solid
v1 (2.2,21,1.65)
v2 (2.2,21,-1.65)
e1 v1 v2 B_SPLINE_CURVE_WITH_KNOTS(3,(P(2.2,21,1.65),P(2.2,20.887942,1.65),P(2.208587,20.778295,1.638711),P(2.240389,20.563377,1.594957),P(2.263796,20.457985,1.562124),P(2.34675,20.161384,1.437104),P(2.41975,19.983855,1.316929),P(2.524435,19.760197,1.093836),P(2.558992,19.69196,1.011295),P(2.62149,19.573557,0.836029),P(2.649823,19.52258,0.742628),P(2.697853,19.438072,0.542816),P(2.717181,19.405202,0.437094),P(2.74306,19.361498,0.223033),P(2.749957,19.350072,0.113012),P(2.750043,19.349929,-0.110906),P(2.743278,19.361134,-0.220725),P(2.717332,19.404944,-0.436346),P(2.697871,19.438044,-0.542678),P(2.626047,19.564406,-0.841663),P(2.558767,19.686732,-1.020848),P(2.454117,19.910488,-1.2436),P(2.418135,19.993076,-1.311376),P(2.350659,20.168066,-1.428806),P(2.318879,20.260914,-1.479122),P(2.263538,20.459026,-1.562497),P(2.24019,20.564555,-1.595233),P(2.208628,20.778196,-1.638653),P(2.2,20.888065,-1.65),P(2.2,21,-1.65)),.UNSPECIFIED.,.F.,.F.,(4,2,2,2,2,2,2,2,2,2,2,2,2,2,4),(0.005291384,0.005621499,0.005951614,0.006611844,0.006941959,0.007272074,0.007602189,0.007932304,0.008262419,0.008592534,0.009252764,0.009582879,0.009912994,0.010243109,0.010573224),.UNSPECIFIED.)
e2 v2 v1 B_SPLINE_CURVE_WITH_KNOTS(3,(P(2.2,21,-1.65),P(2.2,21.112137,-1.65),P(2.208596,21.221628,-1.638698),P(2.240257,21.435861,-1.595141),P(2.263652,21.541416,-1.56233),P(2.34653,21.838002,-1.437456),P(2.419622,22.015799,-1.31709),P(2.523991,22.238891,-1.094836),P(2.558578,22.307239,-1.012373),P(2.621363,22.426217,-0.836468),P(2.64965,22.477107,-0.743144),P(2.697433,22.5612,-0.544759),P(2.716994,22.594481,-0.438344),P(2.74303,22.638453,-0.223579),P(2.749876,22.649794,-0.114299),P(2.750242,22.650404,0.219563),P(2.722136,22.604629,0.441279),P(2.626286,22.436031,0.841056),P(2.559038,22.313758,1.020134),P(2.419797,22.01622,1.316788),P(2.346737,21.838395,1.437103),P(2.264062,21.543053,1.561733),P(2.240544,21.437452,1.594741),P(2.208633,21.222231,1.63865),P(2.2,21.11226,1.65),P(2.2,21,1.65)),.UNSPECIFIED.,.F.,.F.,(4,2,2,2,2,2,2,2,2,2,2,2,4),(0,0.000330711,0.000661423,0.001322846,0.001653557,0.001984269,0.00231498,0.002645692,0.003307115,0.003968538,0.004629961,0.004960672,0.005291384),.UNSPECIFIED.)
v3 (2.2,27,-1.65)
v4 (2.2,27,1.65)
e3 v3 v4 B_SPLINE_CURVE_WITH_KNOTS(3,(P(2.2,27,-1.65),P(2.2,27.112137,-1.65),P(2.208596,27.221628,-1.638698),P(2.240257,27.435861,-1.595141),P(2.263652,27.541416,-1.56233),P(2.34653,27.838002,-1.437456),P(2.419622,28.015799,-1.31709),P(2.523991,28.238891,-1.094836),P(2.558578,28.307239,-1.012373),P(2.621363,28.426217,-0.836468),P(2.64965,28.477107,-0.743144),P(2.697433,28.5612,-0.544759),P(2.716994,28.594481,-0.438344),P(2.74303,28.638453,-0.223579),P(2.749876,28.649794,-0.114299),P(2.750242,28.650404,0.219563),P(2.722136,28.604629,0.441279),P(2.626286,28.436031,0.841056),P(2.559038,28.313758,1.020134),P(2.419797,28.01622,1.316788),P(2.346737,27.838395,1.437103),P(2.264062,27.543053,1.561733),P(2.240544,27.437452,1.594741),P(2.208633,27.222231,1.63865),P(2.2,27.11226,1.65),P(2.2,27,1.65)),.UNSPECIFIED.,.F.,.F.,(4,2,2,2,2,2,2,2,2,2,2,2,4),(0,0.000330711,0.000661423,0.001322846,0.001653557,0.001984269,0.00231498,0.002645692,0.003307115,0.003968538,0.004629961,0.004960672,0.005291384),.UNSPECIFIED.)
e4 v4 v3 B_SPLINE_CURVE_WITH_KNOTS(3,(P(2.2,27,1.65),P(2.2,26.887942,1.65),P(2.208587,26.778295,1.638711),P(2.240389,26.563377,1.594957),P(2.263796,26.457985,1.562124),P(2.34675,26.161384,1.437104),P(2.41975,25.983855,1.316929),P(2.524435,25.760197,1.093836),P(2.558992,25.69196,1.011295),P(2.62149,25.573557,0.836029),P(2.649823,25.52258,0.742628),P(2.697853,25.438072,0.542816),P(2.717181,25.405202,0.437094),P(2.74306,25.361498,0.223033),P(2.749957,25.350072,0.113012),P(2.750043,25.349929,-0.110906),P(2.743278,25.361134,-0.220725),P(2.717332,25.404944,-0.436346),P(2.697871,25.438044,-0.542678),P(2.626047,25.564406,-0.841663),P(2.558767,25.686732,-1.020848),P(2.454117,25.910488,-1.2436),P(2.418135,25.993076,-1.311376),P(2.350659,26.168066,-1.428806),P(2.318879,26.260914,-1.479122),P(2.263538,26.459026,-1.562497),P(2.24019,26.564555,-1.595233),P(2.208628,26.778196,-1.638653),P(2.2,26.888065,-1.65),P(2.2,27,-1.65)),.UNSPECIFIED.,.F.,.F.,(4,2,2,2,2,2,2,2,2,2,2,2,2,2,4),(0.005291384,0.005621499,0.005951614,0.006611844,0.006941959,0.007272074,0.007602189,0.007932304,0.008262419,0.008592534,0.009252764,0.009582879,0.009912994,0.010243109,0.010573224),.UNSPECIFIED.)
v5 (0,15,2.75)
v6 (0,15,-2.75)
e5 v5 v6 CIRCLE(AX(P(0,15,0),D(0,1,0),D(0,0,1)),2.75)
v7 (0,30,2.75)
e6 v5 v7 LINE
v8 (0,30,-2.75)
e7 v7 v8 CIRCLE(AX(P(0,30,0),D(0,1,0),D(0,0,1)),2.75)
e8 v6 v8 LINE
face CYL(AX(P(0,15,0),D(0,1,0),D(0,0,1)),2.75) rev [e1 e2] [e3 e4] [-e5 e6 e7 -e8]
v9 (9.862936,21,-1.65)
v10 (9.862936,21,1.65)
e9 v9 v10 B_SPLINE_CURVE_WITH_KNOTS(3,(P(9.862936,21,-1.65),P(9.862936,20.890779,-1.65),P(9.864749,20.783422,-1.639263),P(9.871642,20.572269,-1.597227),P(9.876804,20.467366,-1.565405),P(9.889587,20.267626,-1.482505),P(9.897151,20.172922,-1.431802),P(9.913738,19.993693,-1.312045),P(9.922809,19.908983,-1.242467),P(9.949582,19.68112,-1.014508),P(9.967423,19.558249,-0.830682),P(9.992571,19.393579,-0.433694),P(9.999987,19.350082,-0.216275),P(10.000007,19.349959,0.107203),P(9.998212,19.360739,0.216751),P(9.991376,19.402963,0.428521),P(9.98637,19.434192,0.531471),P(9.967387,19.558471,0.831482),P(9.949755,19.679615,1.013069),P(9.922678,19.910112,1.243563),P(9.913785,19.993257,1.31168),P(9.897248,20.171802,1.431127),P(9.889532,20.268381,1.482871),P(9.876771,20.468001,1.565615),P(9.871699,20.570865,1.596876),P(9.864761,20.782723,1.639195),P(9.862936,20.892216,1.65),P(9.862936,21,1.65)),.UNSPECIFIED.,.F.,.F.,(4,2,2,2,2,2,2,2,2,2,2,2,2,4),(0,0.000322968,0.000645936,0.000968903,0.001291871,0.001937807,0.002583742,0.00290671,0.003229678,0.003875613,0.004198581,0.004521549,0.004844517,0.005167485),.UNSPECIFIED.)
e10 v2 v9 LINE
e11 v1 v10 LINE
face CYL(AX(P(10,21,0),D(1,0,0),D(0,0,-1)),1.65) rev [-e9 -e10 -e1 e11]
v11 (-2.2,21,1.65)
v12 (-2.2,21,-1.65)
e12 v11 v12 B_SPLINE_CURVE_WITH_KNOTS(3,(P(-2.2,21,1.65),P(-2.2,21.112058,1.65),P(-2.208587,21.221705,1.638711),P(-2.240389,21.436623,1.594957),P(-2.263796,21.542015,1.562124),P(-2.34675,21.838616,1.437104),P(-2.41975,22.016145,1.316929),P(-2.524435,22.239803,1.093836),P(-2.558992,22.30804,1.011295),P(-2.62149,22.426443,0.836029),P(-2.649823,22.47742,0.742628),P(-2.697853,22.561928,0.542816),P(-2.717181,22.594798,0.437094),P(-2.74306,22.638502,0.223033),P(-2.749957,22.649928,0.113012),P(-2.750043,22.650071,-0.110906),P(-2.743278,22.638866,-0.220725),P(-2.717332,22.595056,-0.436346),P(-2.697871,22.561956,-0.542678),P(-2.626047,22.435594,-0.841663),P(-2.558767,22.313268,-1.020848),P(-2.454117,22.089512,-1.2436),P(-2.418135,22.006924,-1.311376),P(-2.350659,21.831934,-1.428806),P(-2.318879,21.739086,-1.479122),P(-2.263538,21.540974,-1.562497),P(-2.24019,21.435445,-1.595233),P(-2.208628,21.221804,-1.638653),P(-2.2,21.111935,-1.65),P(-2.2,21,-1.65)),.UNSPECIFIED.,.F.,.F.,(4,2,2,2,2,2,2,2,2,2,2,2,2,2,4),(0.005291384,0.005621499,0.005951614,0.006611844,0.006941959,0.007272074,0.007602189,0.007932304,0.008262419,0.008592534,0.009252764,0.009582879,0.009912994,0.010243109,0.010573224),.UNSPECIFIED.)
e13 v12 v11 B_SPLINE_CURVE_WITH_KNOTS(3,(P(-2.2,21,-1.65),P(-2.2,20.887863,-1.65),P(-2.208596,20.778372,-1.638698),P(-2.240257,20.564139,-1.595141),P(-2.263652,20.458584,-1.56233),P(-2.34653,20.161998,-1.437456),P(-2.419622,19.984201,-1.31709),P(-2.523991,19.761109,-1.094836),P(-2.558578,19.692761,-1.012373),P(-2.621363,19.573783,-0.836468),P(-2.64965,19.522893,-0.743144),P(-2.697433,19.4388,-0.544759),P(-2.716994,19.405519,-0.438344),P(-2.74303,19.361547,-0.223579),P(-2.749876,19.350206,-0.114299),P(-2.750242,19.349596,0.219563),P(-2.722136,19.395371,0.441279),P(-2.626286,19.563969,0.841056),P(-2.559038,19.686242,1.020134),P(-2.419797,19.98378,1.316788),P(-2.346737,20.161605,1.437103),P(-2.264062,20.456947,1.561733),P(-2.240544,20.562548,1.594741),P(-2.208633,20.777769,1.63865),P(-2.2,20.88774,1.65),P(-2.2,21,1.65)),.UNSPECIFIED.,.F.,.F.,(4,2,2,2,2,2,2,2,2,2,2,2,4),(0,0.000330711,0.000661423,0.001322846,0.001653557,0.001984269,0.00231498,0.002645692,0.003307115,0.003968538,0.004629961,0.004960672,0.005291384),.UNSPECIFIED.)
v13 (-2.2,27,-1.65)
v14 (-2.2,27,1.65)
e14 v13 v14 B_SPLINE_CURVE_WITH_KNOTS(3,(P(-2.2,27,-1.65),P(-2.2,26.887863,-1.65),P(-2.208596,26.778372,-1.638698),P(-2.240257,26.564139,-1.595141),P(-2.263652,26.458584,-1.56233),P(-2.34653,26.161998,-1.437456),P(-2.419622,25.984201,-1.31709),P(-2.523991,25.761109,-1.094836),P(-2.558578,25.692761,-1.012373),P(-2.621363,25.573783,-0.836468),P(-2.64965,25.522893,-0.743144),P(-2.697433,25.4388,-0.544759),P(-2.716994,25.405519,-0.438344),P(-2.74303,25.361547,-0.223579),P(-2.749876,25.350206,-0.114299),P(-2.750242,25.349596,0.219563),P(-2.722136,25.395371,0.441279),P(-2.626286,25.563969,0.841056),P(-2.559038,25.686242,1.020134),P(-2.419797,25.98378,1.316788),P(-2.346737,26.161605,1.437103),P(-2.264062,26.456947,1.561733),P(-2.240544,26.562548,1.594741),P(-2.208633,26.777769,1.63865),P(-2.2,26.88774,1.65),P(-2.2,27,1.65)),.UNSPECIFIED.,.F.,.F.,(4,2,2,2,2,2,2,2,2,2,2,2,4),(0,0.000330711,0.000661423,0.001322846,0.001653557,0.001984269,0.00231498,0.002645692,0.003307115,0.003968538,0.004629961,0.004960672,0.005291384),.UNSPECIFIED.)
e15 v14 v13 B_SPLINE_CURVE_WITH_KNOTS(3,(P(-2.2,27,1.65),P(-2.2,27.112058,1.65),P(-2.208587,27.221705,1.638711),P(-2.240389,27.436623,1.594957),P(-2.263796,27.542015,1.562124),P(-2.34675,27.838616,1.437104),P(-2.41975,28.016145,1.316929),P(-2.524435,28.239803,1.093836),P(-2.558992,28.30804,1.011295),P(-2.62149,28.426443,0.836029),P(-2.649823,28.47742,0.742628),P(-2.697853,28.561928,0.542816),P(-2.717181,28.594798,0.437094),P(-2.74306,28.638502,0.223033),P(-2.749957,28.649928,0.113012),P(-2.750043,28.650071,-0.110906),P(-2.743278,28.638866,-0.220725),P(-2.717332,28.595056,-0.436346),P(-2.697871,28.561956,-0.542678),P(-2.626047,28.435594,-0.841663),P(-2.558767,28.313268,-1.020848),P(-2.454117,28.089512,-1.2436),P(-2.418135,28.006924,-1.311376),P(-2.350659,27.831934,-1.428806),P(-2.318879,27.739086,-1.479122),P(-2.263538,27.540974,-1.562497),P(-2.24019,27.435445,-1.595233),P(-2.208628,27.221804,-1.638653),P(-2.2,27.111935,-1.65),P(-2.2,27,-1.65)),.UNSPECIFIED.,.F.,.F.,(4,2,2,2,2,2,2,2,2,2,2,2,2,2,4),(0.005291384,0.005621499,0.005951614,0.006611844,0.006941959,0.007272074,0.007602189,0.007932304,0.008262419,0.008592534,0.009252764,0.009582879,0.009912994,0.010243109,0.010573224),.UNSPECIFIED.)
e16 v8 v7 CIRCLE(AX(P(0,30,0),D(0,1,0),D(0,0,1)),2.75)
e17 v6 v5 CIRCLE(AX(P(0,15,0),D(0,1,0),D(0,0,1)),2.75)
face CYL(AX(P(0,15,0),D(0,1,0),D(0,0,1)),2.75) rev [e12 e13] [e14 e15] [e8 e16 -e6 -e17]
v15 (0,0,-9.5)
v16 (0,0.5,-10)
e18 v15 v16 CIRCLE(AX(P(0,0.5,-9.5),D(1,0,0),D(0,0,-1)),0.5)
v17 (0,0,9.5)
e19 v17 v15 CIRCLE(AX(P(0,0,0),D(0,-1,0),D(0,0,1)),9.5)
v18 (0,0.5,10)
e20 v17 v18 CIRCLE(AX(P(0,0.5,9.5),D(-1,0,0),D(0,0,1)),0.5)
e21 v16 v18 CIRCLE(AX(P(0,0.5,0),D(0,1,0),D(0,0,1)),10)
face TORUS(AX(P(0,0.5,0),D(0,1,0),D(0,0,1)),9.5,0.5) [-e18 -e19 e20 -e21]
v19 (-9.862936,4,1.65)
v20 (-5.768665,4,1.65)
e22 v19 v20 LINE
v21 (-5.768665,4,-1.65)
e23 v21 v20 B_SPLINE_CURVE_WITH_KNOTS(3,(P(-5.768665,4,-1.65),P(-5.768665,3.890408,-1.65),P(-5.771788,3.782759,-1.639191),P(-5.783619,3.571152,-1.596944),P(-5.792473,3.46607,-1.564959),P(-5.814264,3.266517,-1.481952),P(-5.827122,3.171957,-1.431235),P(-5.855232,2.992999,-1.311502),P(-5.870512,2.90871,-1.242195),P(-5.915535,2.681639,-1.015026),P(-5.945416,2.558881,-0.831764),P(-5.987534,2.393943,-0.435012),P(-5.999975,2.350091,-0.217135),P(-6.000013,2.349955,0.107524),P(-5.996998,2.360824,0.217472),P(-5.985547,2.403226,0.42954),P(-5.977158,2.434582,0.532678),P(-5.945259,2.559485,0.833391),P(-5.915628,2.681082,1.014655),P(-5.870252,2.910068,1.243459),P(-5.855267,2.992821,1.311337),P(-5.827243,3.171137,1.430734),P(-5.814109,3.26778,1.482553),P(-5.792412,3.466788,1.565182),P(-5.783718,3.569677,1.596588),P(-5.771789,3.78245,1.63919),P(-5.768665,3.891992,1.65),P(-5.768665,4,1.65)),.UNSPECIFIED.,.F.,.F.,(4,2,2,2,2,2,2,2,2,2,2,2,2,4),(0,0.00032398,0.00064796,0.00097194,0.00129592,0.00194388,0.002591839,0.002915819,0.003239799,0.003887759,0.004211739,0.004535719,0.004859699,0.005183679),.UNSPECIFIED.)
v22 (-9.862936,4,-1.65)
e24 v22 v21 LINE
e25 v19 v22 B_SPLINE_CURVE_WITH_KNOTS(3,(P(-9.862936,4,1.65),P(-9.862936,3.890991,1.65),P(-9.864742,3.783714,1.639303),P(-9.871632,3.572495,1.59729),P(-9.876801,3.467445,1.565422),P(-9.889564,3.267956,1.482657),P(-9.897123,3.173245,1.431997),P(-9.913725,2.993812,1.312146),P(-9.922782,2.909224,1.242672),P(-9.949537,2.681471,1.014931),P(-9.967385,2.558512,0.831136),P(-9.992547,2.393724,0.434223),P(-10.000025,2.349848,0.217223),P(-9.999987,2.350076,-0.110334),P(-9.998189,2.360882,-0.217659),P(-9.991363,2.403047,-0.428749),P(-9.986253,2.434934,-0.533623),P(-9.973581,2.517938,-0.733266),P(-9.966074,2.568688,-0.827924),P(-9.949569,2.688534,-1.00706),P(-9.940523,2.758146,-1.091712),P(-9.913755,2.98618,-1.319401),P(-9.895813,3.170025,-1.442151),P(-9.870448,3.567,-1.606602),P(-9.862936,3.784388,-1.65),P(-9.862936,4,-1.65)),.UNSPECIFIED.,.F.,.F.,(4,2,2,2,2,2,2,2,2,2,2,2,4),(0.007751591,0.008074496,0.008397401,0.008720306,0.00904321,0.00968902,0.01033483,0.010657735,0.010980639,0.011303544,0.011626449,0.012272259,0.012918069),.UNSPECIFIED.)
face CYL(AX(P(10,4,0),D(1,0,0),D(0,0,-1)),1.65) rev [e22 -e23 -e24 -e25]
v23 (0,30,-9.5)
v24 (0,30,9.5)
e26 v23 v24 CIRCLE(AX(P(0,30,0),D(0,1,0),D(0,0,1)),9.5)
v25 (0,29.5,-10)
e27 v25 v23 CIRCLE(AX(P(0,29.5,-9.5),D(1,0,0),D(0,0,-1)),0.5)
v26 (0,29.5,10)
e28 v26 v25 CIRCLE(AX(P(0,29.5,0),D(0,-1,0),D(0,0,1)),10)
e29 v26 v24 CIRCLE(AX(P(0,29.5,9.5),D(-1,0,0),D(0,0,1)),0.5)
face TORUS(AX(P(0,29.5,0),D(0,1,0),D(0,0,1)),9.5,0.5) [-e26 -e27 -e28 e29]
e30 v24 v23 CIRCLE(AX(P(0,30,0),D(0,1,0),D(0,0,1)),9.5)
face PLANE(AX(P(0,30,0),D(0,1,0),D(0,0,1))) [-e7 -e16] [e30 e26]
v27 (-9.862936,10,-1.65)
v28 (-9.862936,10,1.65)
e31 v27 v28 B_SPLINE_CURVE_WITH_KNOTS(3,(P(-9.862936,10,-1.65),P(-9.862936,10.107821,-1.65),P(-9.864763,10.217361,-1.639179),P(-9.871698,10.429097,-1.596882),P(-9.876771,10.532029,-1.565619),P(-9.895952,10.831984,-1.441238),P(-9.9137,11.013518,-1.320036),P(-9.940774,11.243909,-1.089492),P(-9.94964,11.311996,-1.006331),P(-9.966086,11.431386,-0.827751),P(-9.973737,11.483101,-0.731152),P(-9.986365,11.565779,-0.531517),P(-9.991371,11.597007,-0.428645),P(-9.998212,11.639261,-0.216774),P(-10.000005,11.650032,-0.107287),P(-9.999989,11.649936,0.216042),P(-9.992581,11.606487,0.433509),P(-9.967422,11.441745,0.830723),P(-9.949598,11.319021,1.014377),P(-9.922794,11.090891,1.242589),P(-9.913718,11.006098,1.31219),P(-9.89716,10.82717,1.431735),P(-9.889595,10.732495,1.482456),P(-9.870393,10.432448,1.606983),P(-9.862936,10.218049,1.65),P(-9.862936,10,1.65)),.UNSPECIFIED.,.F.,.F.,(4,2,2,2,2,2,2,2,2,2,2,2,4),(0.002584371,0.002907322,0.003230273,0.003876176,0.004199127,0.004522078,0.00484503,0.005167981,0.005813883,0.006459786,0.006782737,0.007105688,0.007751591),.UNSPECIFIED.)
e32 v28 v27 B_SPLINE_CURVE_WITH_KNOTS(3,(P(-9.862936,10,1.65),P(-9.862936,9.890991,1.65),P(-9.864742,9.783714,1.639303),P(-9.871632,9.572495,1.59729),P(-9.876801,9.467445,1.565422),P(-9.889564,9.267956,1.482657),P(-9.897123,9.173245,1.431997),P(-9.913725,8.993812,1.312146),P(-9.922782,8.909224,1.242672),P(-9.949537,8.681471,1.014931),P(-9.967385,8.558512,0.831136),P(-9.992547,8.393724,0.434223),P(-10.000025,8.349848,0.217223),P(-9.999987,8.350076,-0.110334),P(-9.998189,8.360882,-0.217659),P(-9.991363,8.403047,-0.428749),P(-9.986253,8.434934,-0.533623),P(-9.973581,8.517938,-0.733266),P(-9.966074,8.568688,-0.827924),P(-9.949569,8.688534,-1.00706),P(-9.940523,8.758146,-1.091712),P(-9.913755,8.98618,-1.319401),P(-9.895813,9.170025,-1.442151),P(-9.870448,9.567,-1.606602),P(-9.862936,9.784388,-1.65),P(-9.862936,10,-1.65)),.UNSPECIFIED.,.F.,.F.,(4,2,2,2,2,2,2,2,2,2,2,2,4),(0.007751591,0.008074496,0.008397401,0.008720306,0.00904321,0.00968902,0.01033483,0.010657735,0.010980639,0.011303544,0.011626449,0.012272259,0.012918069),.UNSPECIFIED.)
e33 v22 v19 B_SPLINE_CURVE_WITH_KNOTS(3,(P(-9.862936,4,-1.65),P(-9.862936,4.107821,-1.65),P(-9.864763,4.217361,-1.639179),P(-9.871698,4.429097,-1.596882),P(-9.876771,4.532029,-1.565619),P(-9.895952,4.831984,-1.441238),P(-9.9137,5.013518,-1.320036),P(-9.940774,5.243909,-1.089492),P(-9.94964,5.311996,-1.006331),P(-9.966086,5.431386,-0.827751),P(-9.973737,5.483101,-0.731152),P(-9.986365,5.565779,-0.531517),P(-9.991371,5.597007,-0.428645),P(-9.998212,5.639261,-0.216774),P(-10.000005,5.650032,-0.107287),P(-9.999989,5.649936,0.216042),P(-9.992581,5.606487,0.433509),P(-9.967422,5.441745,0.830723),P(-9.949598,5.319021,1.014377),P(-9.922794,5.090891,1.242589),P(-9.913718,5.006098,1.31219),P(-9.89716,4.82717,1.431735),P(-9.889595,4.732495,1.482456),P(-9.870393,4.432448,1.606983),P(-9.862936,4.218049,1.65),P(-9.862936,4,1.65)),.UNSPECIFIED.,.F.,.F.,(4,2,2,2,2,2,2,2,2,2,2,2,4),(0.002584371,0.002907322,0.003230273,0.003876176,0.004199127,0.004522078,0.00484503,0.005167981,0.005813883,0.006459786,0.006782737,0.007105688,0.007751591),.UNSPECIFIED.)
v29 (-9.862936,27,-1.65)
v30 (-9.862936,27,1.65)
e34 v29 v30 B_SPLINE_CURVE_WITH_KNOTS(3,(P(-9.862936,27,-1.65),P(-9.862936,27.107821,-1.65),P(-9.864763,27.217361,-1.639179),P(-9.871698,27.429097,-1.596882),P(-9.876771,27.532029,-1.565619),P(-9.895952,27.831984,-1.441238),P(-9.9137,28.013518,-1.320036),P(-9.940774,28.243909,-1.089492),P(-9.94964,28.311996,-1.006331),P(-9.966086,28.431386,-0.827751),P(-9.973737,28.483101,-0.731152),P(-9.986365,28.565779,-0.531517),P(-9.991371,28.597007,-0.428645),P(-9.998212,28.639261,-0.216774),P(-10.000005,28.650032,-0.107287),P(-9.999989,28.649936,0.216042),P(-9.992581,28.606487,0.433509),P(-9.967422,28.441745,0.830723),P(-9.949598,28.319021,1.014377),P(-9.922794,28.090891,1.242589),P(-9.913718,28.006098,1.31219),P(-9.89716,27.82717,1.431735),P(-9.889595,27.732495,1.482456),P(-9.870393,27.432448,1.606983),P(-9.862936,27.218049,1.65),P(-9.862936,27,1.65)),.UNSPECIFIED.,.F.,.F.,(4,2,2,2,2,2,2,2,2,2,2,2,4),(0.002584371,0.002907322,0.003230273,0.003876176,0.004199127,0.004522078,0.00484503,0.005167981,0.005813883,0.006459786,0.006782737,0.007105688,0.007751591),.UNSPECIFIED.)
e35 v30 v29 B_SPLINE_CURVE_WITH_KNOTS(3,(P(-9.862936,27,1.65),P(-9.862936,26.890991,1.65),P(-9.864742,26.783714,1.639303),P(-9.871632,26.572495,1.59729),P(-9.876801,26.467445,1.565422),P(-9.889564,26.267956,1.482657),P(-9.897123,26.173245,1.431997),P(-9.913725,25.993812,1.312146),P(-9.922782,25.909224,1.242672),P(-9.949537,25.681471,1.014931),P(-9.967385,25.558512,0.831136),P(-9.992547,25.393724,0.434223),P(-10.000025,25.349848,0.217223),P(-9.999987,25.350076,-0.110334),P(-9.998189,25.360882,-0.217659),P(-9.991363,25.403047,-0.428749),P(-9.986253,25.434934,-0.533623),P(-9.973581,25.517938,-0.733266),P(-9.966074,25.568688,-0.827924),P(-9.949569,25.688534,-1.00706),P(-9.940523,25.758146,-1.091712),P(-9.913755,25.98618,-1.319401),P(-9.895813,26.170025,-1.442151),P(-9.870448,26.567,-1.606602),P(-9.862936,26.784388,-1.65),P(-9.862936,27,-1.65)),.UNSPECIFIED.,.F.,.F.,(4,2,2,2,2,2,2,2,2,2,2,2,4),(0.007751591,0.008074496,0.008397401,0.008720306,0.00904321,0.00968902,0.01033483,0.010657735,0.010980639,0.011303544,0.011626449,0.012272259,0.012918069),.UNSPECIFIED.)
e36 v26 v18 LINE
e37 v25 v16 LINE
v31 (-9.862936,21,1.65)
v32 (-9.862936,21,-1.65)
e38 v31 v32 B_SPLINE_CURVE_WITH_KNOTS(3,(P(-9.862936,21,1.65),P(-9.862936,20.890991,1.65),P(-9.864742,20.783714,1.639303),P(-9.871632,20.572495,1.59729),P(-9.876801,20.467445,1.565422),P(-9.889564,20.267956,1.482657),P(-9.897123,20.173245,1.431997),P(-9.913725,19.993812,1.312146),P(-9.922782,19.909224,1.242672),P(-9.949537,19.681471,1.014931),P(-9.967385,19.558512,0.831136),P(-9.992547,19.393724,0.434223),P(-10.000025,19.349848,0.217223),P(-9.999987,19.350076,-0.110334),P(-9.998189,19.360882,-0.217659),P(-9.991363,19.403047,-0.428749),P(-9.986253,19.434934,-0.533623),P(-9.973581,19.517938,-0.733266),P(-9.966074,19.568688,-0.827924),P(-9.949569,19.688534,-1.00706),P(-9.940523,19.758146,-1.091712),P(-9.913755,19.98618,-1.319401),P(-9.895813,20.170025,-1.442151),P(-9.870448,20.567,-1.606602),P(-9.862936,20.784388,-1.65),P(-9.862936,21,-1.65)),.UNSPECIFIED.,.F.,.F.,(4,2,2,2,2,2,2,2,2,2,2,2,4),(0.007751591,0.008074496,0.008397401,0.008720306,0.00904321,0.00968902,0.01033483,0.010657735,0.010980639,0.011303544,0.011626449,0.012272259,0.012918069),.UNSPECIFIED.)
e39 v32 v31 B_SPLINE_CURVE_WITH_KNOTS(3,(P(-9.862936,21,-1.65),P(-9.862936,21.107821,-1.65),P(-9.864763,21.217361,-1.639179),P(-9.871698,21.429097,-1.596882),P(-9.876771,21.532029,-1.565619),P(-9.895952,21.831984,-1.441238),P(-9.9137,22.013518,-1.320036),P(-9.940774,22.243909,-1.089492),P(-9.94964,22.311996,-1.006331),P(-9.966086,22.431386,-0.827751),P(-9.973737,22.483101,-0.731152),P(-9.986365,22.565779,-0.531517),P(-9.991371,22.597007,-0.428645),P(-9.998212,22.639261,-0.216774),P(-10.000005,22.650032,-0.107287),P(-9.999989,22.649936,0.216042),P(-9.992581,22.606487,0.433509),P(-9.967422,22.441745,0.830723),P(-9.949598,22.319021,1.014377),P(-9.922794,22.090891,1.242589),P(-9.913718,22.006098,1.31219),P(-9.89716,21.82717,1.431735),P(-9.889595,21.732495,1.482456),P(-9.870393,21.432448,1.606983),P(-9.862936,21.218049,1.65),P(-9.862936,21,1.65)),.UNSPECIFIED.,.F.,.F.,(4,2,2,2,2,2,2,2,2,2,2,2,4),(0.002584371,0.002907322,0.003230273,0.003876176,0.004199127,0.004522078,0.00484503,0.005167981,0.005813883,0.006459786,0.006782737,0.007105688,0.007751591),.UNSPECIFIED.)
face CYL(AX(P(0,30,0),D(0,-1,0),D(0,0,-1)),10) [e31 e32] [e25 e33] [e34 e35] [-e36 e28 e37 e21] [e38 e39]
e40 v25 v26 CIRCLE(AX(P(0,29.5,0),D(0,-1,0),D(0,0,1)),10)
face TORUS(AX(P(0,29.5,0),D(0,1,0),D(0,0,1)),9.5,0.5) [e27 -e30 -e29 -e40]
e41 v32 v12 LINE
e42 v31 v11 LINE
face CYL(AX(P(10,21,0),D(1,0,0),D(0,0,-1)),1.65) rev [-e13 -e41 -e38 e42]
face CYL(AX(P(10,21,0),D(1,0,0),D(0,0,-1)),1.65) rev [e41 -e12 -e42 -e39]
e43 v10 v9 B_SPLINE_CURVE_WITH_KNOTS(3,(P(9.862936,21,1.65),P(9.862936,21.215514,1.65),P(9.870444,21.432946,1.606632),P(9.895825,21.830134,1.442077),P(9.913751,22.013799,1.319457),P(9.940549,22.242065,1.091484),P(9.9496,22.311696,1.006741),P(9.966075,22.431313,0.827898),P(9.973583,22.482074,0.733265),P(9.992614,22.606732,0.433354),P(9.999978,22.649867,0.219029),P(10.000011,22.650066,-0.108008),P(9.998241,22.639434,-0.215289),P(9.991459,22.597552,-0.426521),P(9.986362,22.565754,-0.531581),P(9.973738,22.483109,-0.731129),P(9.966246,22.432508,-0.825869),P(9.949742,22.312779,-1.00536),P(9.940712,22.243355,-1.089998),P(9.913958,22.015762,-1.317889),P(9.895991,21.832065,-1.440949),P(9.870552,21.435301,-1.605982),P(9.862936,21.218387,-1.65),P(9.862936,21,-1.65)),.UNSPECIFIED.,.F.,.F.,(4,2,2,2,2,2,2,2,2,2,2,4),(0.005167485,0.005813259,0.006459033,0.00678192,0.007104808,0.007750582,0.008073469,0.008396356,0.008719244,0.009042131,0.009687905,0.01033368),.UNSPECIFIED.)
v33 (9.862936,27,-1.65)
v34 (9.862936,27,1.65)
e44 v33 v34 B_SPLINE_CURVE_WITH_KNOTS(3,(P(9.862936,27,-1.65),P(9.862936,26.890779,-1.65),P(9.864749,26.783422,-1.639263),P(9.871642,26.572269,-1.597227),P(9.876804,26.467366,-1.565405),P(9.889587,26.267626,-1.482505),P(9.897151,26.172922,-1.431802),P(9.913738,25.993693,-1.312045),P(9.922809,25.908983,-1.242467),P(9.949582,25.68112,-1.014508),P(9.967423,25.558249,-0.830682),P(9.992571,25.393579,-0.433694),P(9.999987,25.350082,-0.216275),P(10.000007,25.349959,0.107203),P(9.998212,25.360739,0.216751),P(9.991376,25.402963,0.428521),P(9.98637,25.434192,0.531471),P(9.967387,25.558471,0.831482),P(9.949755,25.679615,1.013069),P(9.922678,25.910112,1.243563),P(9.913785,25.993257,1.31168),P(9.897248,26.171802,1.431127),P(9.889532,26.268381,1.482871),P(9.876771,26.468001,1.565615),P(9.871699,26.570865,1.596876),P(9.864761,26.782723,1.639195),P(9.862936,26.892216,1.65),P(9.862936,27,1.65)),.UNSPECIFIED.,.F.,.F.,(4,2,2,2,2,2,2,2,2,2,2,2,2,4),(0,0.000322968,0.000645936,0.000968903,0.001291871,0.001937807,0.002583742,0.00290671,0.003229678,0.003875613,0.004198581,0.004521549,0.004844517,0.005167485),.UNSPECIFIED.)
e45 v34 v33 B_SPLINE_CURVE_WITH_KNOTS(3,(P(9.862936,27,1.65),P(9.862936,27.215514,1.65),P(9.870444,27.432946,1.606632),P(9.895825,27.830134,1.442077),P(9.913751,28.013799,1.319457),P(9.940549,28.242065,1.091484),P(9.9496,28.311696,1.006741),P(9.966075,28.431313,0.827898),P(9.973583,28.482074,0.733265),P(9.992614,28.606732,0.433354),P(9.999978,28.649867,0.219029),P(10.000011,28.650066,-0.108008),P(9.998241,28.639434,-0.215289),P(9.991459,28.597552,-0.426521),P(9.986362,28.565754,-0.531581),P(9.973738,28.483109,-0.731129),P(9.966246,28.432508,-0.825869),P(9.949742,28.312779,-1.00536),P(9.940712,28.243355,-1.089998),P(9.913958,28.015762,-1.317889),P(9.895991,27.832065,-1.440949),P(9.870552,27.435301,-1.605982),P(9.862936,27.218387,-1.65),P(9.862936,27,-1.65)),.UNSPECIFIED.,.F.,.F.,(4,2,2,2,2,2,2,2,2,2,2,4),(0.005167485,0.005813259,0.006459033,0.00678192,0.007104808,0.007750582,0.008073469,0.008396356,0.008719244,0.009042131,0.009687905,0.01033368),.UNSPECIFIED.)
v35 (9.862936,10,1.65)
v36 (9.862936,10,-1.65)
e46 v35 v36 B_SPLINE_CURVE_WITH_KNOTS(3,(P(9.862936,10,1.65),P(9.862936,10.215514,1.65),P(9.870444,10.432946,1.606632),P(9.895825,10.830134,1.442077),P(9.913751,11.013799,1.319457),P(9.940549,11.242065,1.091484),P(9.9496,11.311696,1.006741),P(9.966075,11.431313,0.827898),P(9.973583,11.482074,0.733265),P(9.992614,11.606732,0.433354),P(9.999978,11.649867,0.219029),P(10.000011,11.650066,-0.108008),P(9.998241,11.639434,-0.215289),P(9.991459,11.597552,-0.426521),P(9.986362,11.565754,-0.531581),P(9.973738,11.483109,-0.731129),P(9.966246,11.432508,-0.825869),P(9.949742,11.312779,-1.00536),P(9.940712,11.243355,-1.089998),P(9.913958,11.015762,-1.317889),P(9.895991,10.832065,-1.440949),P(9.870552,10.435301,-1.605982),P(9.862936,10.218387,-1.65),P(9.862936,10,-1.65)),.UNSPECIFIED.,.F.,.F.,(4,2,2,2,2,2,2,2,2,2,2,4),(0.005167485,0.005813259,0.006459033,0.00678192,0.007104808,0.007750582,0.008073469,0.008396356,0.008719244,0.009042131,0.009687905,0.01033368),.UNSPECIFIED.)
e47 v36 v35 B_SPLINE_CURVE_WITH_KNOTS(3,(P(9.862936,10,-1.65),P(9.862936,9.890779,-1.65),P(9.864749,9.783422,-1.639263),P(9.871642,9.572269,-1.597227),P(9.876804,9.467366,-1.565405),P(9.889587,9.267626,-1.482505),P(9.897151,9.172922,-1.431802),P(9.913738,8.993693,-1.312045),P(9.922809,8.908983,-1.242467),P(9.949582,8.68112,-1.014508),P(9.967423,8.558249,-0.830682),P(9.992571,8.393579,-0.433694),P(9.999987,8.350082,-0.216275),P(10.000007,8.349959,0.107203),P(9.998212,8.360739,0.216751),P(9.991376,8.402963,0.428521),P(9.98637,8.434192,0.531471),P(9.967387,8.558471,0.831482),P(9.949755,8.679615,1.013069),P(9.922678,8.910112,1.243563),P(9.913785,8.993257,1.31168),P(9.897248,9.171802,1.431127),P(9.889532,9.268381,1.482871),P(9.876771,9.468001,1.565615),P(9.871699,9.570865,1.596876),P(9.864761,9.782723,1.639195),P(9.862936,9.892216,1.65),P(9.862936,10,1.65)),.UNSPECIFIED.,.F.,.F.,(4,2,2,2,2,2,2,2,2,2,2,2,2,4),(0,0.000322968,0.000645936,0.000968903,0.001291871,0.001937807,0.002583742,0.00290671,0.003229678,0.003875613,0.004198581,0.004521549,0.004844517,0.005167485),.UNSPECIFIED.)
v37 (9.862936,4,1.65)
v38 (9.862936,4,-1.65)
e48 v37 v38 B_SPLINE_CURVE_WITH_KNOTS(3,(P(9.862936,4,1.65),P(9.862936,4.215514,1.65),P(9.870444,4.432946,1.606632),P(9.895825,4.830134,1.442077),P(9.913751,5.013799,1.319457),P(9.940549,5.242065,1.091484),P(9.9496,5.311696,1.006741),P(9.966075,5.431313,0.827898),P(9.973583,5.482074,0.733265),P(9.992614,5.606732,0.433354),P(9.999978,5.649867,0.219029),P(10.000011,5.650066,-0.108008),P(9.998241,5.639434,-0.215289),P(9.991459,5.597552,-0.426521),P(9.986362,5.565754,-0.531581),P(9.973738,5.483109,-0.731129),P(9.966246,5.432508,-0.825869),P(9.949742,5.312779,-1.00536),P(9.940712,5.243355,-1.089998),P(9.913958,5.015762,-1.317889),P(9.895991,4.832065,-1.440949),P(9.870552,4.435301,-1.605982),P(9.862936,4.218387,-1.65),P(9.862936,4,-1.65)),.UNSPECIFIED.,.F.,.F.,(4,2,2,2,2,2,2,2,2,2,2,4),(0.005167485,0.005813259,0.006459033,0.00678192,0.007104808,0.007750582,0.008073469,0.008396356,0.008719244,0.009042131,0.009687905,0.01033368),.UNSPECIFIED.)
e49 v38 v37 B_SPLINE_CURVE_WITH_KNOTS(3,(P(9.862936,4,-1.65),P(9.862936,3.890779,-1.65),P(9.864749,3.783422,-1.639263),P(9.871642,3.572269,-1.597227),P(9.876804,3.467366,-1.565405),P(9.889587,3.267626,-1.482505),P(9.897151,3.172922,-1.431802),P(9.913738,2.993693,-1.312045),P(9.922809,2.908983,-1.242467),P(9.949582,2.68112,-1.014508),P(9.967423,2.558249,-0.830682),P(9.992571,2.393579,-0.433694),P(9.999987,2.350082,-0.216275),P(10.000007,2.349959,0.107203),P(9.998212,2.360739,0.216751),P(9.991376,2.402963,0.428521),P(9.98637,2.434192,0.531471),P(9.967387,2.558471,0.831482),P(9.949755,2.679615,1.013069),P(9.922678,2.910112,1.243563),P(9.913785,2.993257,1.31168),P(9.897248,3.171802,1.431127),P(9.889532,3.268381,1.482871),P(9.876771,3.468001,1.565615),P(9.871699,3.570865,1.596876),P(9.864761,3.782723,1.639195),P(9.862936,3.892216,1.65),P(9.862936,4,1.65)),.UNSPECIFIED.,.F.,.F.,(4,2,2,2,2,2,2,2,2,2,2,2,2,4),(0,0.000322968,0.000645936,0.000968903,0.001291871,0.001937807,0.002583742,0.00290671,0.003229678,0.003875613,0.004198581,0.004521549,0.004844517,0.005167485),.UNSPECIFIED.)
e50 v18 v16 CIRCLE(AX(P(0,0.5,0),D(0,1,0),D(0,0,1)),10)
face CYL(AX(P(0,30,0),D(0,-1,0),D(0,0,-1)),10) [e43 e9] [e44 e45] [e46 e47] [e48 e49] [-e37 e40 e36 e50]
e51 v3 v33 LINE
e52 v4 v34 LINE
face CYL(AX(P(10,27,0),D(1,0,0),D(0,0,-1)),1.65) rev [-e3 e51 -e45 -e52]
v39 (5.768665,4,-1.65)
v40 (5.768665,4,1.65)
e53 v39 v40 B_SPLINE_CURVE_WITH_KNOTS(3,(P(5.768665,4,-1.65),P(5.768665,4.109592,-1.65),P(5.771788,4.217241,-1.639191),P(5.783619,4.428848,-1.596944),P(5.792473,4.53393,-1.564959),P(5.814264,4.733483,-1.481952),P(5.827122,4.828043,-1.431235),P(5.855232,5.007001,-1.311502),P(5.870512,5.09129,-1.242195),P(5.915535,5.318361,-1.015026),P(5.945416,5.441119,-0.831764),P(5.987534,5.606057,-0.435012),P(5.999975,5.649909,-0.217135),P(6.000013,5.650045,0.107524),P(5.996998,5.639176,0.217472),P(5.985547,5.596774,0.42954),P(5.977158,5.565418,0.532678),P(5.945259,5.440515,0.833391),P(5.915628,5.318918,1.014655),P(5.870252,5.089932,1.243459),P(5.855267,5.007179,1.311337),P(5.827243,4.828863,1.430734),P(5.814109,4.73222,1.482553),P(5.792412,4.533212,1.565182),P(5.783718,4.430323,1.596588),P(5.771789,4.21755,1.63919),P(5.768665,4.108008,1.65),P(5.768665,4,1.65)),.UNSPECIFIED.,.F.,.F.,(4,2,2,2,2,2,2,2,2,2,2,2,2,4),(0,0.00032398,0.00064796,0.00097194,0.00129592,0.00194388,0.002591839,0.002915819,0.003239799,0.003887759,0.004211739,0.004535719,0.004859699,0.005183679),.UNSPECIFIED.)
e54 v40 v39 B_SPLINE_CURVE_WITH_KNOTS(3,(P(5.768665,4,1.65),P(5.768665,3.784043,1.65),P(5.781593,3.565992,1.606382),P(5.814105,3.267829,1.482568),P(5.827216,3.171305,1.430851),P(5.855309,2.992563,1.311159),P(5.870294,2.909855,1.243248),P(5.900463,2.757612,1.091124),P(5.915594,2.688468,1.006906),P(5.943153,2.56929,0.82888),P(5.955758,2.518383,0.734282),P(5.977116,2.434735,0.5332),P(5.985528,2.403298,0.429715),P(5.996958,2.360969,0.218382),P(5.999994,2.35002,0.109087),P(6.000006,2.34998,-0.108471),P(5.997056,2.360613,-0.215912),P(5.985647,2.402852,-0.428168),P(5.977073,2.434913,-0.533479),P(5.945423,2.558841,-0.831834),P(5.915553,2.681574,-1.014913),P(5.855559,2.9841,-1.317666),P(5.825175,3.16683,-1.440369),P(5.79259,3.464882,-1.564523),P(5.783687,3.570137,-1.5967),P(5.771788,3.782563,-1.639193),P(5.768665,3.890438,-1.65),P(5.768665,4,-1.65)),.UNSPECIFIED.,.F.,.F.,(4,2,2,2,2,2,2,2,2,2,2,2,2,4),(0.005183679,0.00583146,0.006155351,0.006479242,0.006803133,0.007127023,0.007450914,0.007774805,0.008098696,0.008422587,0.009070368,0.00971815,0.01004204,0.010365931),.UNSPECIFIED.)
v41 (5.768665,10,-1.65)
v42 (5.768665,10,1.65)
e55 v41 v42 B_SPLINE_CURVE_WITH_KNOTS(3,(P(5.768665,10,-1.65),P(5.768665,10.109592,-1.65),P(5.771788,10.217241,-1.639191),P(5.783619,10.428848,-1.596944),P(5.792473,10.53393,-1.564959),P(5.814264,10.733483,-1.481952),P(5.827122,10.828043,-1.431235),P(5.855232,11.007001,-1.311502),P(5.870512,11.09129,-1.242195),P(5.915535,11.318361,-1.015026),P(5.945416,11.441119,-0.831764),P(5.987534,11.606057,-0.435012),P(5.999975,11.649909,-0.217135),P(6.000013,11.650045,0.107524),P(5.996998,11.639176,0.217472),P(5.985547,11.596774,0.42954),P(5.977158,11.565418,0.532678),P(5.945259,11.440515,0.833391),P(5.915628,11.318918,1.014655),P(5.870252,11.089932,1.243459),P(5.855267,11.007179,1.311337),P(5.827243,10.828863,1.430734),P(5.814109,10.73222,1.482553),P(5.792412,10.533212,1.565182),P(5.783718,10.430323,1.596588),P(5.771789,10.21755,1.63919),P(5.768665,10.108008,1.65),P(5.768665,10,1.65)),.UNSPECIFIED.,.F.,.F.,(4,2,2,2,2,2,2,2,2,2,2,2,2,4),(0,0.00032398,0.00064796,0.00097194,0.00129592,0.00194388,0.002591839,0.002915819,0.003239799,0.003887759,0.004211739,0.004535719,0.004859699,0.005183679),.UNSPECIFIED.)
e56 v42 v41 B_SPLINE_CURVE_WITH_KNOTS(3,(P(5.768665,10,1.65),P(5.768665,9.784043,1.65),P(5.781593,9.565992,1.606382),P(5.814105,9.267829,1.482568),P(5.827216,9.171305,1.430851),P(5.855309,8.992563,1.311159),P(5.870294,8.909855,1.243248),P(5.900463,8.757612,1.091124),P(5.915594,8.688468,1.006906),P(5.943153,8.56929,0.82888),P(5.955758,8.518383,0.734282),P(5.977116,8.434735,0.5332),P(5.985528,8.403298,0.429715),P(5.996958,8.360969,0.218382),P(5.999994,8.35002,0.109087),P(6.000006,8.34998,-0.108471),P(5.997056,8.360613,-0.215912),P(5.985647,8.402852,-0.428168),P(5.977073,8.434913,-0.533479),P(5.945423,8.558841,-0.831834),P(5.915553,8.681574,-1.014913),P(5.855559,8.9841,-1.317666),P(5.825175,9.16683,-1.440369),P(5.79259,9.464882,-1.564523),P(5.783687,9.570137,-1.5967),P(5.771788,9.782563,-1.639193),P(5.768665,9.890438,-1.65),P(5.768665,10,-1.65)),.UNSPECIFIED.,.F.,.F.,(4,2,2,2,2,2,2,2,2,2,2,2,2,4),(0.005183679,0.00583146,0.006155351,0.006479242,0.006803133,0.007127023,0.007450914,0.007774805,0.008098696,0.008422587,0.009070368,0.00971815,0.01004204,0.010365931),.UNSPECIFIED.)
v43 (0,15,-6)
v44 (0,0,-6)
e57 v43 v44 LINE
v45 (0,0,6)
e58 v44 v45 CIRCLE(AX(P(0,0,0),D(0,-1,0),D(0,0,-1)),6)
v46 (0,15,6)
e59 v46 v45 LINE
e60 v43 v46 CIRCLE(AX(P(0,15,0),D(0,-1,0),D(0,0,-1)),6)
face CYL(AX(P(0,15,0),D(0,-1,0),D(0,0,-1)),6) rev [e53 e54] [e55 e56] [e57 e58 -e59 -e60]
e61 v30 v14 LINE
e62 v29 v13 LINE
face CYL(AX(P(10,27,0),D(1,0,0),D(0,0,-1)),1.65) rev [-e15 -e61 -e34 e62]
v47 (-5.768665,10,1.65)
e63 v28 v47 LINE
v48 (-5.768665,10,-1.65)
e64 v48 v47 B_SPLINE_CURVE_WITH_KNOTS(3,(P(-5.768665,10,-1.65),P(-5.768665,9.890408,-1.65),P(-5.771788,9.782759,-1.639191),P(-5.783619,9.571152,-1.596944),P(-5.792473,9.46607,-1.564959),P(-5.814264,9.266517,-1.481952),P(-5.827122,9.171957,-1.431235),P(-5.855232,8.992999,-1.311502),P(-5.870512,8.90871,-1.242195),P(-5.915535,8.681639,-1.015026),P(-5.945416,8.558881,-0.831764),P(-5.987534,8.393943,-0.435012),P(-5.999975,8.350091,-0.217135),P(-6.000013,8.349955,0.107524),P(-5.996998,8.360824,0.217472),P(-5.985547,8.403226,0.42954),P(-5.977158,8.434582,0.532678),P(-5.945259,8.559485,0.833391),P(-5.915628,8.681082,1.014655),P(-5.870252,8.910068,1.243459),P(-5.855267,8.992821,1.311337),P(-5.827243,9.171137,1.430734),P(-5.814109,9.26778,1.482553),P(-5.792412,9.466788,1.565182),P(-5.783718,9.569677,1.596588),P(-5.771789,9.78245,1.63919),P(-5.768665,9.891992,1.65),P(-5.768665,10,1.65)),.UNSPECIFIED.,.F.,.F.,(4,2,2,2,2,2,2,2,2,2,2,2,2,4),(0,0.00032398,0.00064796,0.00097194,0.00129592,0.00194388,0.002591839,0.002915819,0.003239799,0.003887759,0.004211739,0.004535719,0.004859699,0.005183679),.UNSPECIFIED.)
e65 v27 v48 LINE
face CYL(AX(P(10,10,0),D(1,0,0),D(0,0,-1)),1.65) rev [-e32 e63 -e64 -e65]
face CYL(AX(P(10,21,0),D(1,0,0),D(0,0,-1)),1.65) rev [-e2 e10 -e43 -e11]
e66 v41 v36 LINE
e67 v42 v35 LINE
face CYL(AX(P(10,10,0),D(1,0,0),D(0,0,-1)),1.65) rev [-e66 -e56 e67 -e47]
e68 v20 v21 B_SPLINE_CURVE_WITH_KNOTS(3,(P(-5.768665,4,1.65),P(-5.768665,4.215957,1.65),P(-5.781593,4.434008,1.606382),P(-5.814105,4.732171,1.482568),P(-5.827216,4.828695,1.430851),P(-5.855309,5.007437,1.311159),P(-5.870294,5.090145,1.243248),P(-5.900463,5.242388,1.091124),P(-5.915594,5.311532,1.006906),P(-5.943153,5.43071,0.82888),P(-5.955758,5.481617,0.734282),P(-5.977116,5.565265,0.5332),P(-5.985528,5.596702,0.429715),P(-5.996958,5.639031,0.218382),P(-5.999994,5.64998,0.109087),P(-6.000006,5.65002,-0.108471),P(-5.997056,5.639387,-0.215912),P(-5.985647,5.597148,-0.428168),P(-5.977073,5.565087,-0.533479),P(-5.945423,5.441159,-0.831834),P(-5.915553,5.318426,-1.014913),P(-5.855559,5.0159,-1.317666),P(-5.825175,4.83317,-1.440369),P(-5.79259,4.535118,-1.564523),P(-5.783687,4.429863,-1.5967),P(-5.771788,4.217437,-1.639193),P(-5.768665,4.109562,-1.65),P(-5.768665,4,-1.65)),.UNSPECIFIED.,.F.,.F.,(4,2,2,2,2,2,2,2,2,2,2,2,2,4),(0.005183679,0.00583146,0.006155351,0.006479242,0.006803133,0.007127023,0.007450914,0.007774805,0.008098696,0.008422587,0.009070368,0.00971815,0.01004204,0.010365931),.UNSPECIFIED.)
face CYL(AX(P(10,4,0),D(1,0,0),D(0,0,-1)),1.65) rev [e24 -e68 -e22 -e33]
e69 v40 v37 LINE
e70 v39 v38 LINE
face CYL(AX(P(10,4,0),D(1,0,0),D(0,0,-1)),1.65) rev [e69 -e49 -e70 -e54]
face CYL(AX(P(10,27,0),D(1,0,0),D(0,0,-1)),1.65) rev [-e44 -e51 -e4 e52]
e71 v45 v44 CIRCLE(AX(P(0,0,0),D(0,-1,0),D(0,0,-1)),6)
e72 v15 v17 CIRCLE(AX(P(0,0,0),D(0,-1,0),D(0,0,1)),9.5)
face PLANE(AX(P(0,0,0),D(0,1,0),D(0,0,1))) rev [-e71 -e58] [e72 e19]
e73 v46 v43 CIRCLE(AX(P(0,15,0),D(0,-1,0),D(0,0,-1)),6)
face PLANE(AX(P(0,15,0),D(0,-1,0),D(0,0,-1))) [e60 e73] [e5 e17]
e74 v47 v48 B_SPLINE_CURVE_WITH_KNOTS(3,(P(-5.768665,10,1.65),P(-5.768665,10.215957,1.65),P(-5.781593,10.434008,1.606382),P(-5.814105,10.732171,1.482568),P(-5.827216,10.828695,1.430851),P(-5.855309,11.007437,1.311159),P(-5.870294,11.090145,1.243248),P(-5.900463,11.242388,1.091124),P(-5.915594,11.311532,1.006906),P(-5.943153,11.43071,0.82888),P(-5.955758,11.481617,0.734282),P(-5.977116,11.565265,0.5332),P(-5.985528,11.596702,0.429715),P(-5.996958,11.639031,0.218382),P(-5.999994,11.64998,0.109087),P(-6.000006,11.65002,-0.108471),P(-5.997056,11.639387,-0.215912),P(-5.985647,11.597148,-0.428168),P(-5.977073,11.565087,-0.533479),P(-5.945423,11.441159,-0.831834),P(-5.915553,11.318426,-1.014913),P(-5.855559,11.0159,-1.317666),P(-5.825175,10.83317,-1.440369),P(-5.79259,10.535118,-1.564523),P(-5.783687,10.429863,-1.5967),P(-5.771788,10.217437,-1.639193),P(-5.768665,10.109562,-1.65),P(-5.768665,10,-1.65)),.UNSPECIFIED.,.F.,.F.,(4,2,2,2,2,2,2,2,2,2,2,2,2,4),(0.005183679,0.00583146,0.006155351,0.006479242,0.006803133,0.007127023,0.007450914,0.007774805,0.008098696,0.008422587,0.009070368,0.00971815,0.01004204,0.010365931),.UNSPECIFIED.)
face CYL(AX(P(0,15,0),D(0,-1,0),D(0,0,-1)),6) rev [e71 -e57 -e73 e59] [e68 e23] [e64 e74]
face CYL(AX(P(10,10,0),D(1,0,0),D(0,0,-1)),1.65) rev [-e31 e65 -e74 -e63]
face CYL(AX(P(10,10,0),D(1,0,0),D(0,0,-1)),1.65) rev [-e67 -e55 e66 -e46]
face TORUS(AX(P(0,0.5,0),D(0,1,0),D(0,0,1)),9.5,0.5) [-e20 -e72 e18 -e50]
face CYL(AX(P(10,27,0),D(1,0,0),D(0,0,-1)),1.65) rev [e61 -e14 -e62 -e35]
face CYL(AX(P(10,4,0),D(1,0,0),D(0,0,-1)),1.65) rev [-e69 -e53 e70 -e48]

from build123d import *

# Parameters (mm, degrees)
SKETCH1_R           = 10
BOSS_EXTRUDE1_DEPTH = 30
SKETCH2_R           = 2.75
CUT_EXTRUDE1_DEPTH  = 15
SKETCH3_R           = 6
CUT_EXTRUDE2_DEPTH  = 15
M4_TAPPED_HOLE1_D   = 3.3
FILLET1_R           = 0.5


with BuildPart() as part:
    # Sketch1 → Boss-Extrude1 (new body)
    with BuildSketch(Plane(origin=(0, 0, 0), x_dir=(1, 0, 0), z_dir=(0, 1, 0))):
        with Locations(Location((0, 0, 0), (0, 0, 270))):
            Circle(SKETCH1_R)
    extrude(amount=BOSS_EXTRUDE1_DEPTH)

    # Sketch2 → Cut-Extrude1 (cut)
    with BuildSketch(Plane(origin=(0, 30, 0), x_dir=(1, 0, 0), z_dir=(0, 1, 0))):
        with Locations(Location((0, 0, 0), (0, 0, 270))):
            Circle(SKETCH2_R)
    extrude(amount=-CUT_EXTRUDE1_DEPTH, mode=Mode.SUBTRACT)

    # Sketch3 → Cut-Extrude2 (cut)
    with BuildSketch(Plane.XZ):
        with Locations(Location((0, 0, 0), (0, 0, 270))):
            Circle(SKETCH3_R)
    extrude(amount=-CUT_EXTRUDE2_DEPTH, mode=Mode.SUBTRACT)

    # M4 Tapped Hole1 (through all)
    with Locations(Plane(origin=(10, 4, 0), x_dir=(0, 0, 1), z_dir=(1, 0, 0))):
        with Locations((0, 0), (0, -6), (0, -23), (0, -17)):
            Hole(M4_TAPPED_HOLE1_D / 2)

    # Fillet1
    fillet1_edges = [part.edges().sort_by_distance(p)[0] for p in [
        (0, 0, -10),
        (0, 30, -10),
    ]]
    fillet(fillet1_edges, radius=FILLET1_R)


solid = part.part
